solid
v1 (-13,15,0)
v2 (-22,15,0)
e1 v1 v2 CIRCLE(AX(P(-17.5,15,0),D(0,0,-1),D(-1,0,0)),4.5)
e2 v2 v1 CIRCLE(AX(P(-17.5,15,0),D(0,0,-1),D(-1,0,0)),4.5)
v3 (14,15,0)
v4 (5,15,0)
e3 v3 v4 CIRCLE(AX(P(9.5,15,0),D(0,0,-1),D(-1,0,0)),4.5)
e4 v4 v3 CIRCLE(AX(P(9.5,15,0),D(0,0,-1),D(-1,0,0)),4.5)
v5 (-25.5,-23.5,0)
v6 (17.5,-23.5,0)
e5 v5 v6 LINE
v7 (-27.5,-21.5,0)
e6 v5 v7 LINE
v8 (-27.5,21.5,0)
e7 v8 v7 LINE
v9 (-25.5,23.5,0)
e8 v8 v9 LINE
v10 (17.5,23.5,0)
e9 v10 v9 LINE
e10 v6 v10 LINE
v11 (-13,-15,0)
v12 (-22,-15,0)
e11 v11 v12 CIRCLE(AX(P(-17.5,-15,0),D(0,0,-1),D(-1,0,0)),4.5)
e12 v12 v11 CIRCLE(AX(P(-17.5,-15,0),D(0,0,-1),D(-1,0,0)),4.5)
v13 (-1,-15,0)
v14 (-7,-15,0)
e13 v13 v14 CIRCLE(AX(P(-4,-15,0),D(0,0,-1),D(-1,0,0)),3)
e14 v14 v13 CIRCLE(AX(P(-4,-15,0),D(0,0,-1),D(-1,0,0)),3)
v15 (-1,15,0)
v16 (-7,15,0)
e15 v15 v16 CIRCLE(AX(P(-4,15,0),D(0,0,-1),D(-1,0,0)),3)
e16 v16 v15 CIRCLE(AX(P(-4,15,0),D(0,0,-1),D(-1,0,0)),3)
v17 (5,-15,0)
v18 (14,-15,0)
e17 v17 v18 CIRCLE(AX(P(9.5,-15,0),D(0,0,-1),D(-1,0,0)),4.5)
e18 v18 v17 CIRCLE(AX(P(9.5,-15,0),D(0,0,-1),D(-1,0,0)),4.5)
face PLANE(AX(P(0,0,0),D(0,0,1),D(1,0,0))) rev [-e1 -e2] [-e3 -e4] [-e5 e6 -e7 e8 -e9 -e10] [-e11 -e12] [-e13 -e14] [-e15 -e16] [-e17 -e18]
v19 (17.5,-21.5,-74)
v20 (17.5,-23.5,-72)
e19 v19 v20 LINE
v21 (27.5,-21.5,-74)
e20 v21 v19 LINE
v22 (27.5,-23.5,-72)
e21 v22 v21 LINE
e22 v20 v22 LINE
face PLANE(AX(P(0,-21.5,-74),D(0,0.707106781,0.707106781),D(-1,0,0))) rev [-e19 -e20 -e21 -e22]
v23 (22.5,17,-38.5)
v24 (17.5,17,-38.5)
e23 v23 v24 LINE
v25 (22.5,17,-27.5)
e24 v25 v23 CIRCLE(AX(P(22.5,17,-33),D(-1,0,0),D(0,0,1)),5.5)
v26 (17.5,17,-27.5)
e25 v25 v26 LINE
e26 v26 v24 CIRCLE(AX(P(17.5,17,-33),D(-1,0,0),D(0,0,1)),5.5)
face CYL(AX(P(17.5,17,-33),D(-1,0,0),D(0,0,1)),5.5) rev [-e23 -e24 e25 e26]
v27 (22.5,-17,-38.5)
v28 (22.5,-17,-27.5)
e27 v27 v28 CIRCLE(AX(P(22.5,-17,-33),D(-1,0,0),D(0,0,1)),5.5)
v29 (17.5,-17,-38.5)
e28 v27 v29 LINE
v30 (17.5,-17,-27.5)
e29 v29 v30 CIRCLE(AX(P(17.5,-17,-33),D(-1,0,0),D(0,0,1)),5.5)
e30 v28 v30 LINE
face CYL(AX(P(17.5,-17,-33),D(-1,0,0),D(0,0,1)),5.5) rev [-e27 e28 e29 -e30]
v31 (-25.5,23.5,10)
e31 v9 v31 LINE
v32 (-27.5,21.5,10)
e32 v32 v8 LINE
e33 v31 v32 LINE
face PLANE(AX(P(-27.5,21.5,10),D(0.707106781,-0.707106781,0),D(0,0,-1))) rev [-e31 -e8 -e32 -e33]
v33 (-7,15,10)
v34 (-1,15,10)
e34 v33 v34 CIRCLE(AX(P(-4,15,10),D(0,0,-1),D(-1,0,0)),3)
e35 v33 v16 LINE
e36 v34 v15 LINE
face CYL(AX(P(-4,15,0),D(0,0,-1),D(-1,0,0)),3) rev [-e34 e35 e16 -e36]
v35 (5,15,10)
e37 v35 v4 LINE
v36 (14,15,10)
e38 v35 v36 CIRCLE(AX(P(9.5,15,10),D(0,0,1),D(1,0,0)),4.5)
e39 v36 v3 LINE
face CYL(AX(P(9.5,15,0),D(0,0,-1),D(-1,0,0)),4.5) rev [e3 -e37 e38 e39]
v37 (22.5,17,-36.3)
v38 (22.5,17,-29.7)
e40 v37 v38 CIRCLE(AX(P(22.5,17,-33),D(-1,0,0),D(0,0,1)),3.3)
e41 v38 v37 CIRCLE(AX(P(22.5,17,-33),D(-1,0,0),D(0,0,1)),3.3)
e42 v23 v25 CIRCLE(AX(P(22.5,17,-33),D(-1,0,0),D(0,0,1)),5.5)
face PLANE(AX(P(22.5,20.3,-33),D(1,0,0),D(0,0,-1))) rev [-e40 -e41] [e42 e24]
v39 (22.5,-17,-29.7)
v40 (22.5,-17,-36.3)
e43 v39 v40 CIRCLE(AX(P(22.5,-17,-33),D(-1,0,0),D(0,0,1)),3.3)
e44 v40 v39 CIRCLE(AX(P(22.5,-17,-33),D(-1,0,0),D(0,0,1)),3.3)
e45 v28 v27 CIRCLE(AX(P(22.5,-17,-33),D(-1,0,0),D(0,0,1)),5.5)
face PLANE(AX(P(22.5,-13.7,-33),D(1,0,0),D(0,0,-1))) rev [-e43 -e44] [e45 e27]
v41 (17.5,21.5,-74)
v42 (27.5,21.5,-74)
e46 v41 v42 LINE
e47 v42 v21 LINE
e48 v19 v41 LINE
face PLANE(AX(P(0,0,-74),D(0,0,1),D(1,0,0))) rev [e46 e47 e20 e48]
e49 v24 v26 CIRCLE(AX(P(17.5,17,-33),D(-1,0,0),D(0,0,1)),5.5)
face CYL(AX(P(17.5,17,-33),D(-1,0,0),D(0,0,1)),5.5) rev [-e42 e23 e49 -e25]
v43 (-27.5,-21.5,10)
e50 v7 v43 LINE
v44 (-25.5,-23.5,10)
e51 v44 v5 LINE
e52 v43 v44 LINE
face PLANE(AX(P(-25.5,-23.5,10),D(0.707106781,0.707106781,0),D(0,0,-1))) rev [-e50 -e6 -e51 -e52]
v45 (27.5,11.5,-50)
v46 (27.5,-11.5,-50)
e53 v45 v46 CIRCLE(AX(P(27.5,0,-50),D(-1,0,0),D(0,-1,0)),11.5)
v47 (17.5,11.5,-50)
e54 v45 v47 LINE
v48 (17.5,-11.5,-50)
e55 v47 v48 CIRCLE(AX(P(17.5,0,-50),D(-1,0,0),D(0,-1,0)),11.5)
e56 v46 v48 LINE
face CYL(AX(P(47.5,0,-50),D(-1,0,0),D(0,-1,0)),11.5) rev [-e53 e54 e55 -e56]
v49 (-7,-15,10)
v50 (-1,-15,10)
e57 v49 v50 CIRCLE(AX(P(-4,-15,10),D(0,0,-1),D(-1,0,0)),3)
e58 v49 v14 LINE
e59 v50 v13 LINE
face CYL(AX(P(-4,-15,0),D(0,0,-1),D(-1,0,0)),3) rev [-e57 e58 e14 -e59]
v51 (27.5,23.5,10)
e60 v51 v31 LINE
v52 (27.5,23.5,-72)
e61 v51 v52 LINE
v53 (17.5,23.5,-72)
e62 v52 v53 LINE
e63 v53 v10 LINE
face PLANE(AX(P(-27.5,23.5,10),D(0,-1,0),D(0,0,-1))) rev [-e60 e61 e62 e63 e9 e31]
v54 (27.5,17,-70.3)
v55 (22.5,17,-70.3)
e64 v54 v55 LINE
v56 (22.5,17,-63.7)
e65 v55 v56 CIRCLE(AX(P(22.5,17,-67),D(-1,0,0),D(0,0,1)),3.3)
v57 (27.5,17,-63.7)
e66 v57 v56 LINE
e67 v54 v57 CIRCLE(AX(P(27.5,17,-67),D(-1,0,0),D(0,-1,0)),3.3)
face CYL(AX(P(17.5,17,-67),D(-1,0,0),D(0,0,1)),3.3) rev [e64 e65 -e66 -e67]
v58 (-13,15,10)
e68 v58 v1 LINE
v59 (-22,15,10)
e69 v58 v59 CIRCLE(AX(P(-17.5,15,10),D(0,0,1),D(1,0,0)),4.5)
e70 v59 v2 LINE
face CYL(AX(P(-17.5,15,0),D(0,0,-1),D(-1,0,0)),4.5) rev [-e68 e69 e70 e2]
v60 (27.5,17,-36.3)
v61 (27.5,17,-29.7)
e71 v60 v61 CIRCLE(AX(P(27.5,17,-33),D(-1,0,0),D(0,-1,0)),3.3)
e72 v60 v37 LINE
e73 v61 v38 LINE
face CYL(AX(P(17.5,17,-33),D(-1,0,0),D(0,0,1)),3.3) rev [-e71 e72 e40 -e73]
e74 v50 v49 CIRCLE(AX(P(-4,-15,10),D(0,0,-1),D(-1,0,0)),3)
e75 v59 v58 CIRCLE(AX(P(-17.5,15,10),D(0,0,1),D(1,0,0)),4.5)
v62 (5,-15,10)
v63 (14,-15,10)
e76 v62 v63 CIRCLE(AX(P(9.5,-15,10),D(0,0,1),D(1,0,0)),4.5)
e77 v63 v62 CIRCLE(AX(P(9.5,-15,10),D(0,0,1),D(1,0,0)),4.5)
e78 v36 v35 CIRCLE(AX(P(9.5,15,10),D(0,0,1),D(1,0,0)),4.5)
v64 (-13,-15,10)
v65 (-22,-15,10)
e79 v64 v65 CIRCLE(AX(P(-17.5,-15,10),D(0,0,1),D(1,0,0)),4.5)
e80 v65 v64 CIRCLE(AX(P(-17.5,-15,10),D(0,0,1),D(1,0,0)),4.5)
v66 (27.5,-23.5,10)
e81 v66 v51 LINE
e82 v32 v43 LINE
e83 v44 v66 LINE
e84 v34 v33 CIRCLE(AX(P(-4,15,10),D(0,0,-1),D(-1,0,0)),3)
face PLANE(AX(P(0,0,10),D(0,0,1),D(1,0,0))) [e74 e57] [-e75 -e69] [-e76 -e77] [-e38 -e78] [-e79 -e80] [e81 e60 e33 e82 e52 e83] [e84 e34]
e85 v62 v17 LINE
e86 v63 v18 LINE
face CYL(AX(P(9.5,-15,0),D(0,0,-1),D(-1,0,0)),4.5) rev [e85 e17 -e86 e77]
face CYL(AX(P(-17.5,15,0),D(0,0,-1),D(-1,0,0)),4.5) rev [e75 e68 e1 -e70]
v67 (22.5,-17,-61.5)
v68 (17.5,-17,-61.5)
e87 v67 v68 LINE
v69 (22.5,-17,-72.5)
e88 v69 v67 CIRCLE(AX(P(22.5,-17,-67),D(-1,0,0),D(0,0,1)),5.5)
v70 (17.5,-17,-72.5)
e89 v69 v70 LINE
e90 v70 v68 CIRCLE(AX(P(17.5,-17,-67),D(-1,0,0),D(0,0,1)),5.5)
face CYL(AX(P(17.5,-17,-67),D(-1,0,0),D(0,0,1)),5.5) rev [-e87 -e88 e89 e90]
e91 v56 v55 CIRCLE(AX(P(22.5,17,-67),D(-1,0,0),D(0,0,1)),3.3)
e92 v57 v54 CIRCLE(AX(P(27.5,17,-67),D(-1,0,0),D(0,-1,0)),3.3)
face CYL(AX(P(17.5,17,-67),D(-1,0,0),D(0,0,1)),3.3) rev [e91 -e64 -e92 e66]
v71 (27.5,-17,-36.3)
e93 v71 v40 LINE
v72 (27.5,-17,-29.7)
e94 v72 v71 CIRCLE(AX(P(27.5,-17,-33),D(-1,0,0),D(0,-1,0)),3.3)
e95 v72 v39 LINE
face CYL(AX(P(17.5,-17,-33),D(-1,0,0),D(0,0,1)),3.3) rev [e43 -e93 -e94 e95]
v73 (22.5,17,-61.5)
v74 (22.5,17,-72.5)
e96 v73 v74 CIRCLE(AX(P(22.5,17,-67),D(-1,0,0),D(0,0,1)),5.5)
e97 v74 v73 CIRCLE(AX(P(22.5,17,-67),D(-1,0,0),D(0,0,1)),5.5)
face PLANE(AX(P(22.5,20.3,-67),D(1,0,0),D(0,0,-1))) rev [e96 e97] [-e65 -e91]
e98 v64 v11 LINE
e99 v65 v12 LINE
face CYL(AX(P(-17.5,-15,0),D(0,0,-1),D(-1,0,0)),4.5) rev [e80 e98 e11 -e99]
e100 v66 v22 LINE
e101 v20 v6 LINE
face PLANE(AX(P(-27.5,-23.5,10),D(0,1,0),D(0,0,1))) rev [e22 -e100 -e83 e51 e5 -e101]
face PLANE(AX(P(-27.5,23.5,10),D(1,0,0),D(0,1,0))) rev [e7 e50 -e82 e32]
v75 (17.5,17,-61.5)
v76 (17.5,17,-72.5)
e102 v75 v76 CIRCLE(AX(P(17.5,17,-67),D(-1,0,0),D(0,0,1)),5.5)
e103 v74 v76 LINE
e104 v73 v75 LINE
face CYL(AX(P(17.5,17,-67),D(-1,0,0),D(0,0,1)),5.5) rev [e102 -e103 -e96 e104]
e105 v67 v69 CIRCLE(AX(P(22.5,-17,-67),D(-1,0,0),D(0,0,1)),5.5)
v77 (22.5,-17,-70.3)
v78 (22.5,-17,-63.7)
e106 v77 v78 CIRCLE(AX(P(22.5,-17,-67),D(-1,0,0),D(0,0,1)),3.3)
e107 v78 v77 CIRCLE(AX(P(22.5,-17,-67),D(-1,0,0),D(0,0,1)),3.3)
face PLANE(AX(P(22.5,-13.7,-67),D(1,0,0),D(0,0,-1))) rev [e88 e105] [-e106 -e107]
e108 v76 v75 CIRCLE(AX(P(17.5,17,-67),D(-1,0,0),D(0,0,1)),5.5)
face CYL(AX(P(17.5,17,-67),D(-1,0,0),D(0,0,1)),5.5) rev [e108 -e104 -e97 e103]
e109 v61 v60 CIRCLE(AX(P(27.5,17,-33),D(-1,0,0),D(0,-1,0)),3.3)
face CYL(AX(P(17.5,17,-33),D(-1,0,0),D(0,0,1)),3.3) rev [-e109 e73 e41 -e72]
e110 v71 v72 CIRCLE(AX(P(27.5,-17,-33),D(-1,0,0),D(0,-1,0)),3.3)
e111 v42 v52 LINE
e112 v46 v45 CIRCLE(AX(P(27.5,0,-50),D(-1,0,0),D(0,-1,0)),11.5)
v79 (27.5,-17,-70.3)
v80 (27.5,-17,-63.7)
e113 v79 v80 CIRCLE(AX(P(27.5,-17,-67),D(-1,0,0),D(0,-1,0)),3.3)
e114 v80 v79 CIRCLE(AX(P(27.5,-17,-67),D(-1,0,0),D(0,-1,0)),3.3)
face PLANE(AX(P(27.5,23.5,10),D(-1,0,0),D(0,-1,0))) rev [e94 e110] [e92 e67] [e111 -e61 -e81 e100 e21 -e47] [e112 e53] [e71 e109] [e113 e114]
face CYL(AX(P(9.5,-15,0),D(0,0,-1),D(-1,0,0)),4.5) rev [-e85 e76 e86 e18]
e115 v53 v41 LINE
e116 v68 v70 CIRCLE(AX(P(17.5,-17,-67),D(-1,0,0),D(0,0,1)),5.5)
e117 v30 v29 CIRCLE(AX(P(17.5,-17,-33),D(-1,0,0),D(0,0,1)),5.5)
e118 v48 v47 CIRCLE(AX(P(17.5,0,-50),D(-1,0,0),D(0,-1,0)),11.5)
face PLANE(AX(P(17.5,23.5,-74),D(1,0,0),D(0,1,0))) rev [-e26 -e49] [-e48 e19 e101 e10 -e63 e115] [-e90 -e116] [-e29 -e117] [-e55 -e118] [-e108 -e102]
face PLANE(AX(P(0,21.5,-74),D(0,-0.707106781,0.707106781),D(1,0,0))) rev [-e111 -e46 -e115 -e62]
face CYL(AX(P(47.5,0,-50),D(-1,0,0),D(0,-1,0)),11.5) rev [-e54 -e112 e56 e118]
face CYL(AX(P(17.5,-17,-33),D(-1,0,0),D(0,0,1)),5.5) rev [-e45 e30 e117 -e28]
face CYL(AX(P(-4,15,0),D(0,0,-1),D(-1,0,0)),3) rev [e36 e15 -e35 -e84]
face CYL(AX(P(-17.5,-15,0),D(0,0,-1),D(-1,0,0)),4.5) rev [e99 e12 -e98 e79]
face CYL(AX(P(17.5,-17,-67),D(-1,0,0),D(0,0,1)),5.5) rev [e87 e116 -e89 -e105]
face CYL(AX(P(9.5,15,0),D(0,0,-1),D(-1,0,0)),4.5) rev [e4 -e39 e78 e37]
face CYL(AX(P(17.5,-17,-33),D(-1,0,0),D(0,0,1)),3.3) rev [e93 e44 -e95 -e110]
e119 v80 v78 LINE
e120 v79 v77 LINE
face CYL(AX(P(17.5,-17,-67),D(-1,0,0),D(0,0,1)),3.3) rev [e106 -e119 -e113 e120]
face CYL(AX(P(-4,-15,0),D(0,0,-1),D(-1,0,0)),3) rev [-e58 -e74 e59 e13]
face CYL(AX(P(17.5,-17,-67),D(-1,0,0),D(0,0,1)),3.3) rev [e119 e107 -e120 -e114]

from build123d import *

# Parameters (mm, degrees)
SKETCH1_W                    = 55
SKETCH1_H                    = 47
BOSS_EXTRUDE1_DEPTH          = 10
SKETCH4_W                    = 10
SKETCH4_H                    = 47
BOSS_EXTRUDE2_DEPTH          = 74
M8_CLEARANCE_HOLE1_D         = 9
M8_CLEARANCE_HOLE1_DEPTH     = 121
M8_CLEARANCE_HOLE1_TIP       = 2.703872786
CHAMFER1_SIZE                = 2
SKETCH8_R                    = 11.5
CUT_EXTRUDE1_DEPTH           = 30
CHAMFER2_SIZE                = 2
SIZE_MM_BLIND_DOWEL_HOLE_1_D = 6
CIRPATTERN1_COUNT            = 4


with BuildPart() as part:
    # Sketch1 → Boss-Extrude1 (new body)
    with BuildSketch(Plane.XY):
        Rectangle(SKETCH1_W, SKETCH1_H)
    extrude(amount=BOSS_EXTRUDE1_DEPTH)

    # Sketch4 → Boss-Extrude2 (add)
    with BuildSketch(Plane(origin=(0, 0, 0), x_dir=(-1, 0, 0), z_dir=(0, 0, -1))):
        with Locations((-22.5, 0)):
            Rectangle(SKETCH4_W, SKETCH4_H)
    extrude(amount=BOSS_EXTRUDE2_DEPTH)

    # M8 Clearance Hole1
    with Locations(Plane(origin=(0, 0, 0), x_dir=(-1, 0, 0), z_dir=(0, 0, -1))):
        with Locations((17.5, -15), (17.5, 15), (-9.5, -15), (-9.5, 15)):
            Hole(M8_CLEARANCE_HOLE1_D / 2, depth=M8_CLEARANCE_HOLE1_DEPTH)
            with Locations((0, 0, -(M8_CLEARANCE_HOLE1_DEPTH + M8_CLEARANCE_HOLE1_TIP / 2))):  # 118° drill point
                Cone(0, M8_CLEARANCE_HOLE1_D / 2, M8_CLEARANCE_HOLE1_TIP, mode=Mode.SUBTRACT)

    # Chamfer1
    chamfer1_edges = [part.edges().sort_by_distance(p)[0] for p in [
        (-27.5, -23.5, 5),
        (-27.5, 23.5, 5),
    ]]
    chamfer(chamfer1_edges, length=CHAMFER1_SIZE)

    # Sketch8 → Cut-Extrude1 (cut)
    with BuildSketch(Plane.ZY.offset(-17.5)):
        with Locations(Location((-50, 0, 0), (0, 0, 270))):
            Circle(SKETCH8_R)
    extrude(amount=-CUT_EXTRUDE1_DEPTH, mode=Mode.SUBTRACT)

    # Chamfer2
    chamfer2_edges = [part.edges().sort_by_distance(p)[0] for p in [
        (22.5, 23.5, -74),
        (22.5, -23.5, -74),
    ]]
    chamfer(chamfer2_edges, length=CHAMFER2_SIZE)

    # Size mm blind dowel hole 1 (through all)
    with Locations(Plane(origin=(0, 0, 0), x_dir=(-1, 0, 0), z_dir=(0, 0, -1))):
        with Locations((4, -15), (4, 15)):
            Hole(SIZE_MM_BLIND_DOWEL_HOLE_1_D / 2)

    # Sketch14 → Hole size (per socket head cap screw type)1 (revolve, cut)
    with BuildSketch(Plane(origin=(17.5, -17, -67), x_dir=(0, 0, 1), z_dir=(0, 1, 0))):
        Polygon((0, 0), (0, 34.732840043), (3.3, 32.75), (3.3, 5), (5.5, 5), (5.5, 0), align=None)
    hole_size_per_socket_head_cap_screw_typ = revolve(axis=Axis((11.15, -17, -67), (1, 0, 0)), mode=Mode.SUBTRACT)

    # CirPattern1: Hole size (per socket head cap screw type)1 ×4 about axis
    cirpattern1_axis = Axis((0, 0, -50), (1, 0, 0))
    for i in range(1, CIRPATTERN1_COUNT):
        add(hole_size_per_socket_head_cap_screw_typ.rotate(cirpattern1_axis, i * 360 / CIRPATTERN1_COUNT), mode=Mode.SUBTRACT)


solid = part.part
